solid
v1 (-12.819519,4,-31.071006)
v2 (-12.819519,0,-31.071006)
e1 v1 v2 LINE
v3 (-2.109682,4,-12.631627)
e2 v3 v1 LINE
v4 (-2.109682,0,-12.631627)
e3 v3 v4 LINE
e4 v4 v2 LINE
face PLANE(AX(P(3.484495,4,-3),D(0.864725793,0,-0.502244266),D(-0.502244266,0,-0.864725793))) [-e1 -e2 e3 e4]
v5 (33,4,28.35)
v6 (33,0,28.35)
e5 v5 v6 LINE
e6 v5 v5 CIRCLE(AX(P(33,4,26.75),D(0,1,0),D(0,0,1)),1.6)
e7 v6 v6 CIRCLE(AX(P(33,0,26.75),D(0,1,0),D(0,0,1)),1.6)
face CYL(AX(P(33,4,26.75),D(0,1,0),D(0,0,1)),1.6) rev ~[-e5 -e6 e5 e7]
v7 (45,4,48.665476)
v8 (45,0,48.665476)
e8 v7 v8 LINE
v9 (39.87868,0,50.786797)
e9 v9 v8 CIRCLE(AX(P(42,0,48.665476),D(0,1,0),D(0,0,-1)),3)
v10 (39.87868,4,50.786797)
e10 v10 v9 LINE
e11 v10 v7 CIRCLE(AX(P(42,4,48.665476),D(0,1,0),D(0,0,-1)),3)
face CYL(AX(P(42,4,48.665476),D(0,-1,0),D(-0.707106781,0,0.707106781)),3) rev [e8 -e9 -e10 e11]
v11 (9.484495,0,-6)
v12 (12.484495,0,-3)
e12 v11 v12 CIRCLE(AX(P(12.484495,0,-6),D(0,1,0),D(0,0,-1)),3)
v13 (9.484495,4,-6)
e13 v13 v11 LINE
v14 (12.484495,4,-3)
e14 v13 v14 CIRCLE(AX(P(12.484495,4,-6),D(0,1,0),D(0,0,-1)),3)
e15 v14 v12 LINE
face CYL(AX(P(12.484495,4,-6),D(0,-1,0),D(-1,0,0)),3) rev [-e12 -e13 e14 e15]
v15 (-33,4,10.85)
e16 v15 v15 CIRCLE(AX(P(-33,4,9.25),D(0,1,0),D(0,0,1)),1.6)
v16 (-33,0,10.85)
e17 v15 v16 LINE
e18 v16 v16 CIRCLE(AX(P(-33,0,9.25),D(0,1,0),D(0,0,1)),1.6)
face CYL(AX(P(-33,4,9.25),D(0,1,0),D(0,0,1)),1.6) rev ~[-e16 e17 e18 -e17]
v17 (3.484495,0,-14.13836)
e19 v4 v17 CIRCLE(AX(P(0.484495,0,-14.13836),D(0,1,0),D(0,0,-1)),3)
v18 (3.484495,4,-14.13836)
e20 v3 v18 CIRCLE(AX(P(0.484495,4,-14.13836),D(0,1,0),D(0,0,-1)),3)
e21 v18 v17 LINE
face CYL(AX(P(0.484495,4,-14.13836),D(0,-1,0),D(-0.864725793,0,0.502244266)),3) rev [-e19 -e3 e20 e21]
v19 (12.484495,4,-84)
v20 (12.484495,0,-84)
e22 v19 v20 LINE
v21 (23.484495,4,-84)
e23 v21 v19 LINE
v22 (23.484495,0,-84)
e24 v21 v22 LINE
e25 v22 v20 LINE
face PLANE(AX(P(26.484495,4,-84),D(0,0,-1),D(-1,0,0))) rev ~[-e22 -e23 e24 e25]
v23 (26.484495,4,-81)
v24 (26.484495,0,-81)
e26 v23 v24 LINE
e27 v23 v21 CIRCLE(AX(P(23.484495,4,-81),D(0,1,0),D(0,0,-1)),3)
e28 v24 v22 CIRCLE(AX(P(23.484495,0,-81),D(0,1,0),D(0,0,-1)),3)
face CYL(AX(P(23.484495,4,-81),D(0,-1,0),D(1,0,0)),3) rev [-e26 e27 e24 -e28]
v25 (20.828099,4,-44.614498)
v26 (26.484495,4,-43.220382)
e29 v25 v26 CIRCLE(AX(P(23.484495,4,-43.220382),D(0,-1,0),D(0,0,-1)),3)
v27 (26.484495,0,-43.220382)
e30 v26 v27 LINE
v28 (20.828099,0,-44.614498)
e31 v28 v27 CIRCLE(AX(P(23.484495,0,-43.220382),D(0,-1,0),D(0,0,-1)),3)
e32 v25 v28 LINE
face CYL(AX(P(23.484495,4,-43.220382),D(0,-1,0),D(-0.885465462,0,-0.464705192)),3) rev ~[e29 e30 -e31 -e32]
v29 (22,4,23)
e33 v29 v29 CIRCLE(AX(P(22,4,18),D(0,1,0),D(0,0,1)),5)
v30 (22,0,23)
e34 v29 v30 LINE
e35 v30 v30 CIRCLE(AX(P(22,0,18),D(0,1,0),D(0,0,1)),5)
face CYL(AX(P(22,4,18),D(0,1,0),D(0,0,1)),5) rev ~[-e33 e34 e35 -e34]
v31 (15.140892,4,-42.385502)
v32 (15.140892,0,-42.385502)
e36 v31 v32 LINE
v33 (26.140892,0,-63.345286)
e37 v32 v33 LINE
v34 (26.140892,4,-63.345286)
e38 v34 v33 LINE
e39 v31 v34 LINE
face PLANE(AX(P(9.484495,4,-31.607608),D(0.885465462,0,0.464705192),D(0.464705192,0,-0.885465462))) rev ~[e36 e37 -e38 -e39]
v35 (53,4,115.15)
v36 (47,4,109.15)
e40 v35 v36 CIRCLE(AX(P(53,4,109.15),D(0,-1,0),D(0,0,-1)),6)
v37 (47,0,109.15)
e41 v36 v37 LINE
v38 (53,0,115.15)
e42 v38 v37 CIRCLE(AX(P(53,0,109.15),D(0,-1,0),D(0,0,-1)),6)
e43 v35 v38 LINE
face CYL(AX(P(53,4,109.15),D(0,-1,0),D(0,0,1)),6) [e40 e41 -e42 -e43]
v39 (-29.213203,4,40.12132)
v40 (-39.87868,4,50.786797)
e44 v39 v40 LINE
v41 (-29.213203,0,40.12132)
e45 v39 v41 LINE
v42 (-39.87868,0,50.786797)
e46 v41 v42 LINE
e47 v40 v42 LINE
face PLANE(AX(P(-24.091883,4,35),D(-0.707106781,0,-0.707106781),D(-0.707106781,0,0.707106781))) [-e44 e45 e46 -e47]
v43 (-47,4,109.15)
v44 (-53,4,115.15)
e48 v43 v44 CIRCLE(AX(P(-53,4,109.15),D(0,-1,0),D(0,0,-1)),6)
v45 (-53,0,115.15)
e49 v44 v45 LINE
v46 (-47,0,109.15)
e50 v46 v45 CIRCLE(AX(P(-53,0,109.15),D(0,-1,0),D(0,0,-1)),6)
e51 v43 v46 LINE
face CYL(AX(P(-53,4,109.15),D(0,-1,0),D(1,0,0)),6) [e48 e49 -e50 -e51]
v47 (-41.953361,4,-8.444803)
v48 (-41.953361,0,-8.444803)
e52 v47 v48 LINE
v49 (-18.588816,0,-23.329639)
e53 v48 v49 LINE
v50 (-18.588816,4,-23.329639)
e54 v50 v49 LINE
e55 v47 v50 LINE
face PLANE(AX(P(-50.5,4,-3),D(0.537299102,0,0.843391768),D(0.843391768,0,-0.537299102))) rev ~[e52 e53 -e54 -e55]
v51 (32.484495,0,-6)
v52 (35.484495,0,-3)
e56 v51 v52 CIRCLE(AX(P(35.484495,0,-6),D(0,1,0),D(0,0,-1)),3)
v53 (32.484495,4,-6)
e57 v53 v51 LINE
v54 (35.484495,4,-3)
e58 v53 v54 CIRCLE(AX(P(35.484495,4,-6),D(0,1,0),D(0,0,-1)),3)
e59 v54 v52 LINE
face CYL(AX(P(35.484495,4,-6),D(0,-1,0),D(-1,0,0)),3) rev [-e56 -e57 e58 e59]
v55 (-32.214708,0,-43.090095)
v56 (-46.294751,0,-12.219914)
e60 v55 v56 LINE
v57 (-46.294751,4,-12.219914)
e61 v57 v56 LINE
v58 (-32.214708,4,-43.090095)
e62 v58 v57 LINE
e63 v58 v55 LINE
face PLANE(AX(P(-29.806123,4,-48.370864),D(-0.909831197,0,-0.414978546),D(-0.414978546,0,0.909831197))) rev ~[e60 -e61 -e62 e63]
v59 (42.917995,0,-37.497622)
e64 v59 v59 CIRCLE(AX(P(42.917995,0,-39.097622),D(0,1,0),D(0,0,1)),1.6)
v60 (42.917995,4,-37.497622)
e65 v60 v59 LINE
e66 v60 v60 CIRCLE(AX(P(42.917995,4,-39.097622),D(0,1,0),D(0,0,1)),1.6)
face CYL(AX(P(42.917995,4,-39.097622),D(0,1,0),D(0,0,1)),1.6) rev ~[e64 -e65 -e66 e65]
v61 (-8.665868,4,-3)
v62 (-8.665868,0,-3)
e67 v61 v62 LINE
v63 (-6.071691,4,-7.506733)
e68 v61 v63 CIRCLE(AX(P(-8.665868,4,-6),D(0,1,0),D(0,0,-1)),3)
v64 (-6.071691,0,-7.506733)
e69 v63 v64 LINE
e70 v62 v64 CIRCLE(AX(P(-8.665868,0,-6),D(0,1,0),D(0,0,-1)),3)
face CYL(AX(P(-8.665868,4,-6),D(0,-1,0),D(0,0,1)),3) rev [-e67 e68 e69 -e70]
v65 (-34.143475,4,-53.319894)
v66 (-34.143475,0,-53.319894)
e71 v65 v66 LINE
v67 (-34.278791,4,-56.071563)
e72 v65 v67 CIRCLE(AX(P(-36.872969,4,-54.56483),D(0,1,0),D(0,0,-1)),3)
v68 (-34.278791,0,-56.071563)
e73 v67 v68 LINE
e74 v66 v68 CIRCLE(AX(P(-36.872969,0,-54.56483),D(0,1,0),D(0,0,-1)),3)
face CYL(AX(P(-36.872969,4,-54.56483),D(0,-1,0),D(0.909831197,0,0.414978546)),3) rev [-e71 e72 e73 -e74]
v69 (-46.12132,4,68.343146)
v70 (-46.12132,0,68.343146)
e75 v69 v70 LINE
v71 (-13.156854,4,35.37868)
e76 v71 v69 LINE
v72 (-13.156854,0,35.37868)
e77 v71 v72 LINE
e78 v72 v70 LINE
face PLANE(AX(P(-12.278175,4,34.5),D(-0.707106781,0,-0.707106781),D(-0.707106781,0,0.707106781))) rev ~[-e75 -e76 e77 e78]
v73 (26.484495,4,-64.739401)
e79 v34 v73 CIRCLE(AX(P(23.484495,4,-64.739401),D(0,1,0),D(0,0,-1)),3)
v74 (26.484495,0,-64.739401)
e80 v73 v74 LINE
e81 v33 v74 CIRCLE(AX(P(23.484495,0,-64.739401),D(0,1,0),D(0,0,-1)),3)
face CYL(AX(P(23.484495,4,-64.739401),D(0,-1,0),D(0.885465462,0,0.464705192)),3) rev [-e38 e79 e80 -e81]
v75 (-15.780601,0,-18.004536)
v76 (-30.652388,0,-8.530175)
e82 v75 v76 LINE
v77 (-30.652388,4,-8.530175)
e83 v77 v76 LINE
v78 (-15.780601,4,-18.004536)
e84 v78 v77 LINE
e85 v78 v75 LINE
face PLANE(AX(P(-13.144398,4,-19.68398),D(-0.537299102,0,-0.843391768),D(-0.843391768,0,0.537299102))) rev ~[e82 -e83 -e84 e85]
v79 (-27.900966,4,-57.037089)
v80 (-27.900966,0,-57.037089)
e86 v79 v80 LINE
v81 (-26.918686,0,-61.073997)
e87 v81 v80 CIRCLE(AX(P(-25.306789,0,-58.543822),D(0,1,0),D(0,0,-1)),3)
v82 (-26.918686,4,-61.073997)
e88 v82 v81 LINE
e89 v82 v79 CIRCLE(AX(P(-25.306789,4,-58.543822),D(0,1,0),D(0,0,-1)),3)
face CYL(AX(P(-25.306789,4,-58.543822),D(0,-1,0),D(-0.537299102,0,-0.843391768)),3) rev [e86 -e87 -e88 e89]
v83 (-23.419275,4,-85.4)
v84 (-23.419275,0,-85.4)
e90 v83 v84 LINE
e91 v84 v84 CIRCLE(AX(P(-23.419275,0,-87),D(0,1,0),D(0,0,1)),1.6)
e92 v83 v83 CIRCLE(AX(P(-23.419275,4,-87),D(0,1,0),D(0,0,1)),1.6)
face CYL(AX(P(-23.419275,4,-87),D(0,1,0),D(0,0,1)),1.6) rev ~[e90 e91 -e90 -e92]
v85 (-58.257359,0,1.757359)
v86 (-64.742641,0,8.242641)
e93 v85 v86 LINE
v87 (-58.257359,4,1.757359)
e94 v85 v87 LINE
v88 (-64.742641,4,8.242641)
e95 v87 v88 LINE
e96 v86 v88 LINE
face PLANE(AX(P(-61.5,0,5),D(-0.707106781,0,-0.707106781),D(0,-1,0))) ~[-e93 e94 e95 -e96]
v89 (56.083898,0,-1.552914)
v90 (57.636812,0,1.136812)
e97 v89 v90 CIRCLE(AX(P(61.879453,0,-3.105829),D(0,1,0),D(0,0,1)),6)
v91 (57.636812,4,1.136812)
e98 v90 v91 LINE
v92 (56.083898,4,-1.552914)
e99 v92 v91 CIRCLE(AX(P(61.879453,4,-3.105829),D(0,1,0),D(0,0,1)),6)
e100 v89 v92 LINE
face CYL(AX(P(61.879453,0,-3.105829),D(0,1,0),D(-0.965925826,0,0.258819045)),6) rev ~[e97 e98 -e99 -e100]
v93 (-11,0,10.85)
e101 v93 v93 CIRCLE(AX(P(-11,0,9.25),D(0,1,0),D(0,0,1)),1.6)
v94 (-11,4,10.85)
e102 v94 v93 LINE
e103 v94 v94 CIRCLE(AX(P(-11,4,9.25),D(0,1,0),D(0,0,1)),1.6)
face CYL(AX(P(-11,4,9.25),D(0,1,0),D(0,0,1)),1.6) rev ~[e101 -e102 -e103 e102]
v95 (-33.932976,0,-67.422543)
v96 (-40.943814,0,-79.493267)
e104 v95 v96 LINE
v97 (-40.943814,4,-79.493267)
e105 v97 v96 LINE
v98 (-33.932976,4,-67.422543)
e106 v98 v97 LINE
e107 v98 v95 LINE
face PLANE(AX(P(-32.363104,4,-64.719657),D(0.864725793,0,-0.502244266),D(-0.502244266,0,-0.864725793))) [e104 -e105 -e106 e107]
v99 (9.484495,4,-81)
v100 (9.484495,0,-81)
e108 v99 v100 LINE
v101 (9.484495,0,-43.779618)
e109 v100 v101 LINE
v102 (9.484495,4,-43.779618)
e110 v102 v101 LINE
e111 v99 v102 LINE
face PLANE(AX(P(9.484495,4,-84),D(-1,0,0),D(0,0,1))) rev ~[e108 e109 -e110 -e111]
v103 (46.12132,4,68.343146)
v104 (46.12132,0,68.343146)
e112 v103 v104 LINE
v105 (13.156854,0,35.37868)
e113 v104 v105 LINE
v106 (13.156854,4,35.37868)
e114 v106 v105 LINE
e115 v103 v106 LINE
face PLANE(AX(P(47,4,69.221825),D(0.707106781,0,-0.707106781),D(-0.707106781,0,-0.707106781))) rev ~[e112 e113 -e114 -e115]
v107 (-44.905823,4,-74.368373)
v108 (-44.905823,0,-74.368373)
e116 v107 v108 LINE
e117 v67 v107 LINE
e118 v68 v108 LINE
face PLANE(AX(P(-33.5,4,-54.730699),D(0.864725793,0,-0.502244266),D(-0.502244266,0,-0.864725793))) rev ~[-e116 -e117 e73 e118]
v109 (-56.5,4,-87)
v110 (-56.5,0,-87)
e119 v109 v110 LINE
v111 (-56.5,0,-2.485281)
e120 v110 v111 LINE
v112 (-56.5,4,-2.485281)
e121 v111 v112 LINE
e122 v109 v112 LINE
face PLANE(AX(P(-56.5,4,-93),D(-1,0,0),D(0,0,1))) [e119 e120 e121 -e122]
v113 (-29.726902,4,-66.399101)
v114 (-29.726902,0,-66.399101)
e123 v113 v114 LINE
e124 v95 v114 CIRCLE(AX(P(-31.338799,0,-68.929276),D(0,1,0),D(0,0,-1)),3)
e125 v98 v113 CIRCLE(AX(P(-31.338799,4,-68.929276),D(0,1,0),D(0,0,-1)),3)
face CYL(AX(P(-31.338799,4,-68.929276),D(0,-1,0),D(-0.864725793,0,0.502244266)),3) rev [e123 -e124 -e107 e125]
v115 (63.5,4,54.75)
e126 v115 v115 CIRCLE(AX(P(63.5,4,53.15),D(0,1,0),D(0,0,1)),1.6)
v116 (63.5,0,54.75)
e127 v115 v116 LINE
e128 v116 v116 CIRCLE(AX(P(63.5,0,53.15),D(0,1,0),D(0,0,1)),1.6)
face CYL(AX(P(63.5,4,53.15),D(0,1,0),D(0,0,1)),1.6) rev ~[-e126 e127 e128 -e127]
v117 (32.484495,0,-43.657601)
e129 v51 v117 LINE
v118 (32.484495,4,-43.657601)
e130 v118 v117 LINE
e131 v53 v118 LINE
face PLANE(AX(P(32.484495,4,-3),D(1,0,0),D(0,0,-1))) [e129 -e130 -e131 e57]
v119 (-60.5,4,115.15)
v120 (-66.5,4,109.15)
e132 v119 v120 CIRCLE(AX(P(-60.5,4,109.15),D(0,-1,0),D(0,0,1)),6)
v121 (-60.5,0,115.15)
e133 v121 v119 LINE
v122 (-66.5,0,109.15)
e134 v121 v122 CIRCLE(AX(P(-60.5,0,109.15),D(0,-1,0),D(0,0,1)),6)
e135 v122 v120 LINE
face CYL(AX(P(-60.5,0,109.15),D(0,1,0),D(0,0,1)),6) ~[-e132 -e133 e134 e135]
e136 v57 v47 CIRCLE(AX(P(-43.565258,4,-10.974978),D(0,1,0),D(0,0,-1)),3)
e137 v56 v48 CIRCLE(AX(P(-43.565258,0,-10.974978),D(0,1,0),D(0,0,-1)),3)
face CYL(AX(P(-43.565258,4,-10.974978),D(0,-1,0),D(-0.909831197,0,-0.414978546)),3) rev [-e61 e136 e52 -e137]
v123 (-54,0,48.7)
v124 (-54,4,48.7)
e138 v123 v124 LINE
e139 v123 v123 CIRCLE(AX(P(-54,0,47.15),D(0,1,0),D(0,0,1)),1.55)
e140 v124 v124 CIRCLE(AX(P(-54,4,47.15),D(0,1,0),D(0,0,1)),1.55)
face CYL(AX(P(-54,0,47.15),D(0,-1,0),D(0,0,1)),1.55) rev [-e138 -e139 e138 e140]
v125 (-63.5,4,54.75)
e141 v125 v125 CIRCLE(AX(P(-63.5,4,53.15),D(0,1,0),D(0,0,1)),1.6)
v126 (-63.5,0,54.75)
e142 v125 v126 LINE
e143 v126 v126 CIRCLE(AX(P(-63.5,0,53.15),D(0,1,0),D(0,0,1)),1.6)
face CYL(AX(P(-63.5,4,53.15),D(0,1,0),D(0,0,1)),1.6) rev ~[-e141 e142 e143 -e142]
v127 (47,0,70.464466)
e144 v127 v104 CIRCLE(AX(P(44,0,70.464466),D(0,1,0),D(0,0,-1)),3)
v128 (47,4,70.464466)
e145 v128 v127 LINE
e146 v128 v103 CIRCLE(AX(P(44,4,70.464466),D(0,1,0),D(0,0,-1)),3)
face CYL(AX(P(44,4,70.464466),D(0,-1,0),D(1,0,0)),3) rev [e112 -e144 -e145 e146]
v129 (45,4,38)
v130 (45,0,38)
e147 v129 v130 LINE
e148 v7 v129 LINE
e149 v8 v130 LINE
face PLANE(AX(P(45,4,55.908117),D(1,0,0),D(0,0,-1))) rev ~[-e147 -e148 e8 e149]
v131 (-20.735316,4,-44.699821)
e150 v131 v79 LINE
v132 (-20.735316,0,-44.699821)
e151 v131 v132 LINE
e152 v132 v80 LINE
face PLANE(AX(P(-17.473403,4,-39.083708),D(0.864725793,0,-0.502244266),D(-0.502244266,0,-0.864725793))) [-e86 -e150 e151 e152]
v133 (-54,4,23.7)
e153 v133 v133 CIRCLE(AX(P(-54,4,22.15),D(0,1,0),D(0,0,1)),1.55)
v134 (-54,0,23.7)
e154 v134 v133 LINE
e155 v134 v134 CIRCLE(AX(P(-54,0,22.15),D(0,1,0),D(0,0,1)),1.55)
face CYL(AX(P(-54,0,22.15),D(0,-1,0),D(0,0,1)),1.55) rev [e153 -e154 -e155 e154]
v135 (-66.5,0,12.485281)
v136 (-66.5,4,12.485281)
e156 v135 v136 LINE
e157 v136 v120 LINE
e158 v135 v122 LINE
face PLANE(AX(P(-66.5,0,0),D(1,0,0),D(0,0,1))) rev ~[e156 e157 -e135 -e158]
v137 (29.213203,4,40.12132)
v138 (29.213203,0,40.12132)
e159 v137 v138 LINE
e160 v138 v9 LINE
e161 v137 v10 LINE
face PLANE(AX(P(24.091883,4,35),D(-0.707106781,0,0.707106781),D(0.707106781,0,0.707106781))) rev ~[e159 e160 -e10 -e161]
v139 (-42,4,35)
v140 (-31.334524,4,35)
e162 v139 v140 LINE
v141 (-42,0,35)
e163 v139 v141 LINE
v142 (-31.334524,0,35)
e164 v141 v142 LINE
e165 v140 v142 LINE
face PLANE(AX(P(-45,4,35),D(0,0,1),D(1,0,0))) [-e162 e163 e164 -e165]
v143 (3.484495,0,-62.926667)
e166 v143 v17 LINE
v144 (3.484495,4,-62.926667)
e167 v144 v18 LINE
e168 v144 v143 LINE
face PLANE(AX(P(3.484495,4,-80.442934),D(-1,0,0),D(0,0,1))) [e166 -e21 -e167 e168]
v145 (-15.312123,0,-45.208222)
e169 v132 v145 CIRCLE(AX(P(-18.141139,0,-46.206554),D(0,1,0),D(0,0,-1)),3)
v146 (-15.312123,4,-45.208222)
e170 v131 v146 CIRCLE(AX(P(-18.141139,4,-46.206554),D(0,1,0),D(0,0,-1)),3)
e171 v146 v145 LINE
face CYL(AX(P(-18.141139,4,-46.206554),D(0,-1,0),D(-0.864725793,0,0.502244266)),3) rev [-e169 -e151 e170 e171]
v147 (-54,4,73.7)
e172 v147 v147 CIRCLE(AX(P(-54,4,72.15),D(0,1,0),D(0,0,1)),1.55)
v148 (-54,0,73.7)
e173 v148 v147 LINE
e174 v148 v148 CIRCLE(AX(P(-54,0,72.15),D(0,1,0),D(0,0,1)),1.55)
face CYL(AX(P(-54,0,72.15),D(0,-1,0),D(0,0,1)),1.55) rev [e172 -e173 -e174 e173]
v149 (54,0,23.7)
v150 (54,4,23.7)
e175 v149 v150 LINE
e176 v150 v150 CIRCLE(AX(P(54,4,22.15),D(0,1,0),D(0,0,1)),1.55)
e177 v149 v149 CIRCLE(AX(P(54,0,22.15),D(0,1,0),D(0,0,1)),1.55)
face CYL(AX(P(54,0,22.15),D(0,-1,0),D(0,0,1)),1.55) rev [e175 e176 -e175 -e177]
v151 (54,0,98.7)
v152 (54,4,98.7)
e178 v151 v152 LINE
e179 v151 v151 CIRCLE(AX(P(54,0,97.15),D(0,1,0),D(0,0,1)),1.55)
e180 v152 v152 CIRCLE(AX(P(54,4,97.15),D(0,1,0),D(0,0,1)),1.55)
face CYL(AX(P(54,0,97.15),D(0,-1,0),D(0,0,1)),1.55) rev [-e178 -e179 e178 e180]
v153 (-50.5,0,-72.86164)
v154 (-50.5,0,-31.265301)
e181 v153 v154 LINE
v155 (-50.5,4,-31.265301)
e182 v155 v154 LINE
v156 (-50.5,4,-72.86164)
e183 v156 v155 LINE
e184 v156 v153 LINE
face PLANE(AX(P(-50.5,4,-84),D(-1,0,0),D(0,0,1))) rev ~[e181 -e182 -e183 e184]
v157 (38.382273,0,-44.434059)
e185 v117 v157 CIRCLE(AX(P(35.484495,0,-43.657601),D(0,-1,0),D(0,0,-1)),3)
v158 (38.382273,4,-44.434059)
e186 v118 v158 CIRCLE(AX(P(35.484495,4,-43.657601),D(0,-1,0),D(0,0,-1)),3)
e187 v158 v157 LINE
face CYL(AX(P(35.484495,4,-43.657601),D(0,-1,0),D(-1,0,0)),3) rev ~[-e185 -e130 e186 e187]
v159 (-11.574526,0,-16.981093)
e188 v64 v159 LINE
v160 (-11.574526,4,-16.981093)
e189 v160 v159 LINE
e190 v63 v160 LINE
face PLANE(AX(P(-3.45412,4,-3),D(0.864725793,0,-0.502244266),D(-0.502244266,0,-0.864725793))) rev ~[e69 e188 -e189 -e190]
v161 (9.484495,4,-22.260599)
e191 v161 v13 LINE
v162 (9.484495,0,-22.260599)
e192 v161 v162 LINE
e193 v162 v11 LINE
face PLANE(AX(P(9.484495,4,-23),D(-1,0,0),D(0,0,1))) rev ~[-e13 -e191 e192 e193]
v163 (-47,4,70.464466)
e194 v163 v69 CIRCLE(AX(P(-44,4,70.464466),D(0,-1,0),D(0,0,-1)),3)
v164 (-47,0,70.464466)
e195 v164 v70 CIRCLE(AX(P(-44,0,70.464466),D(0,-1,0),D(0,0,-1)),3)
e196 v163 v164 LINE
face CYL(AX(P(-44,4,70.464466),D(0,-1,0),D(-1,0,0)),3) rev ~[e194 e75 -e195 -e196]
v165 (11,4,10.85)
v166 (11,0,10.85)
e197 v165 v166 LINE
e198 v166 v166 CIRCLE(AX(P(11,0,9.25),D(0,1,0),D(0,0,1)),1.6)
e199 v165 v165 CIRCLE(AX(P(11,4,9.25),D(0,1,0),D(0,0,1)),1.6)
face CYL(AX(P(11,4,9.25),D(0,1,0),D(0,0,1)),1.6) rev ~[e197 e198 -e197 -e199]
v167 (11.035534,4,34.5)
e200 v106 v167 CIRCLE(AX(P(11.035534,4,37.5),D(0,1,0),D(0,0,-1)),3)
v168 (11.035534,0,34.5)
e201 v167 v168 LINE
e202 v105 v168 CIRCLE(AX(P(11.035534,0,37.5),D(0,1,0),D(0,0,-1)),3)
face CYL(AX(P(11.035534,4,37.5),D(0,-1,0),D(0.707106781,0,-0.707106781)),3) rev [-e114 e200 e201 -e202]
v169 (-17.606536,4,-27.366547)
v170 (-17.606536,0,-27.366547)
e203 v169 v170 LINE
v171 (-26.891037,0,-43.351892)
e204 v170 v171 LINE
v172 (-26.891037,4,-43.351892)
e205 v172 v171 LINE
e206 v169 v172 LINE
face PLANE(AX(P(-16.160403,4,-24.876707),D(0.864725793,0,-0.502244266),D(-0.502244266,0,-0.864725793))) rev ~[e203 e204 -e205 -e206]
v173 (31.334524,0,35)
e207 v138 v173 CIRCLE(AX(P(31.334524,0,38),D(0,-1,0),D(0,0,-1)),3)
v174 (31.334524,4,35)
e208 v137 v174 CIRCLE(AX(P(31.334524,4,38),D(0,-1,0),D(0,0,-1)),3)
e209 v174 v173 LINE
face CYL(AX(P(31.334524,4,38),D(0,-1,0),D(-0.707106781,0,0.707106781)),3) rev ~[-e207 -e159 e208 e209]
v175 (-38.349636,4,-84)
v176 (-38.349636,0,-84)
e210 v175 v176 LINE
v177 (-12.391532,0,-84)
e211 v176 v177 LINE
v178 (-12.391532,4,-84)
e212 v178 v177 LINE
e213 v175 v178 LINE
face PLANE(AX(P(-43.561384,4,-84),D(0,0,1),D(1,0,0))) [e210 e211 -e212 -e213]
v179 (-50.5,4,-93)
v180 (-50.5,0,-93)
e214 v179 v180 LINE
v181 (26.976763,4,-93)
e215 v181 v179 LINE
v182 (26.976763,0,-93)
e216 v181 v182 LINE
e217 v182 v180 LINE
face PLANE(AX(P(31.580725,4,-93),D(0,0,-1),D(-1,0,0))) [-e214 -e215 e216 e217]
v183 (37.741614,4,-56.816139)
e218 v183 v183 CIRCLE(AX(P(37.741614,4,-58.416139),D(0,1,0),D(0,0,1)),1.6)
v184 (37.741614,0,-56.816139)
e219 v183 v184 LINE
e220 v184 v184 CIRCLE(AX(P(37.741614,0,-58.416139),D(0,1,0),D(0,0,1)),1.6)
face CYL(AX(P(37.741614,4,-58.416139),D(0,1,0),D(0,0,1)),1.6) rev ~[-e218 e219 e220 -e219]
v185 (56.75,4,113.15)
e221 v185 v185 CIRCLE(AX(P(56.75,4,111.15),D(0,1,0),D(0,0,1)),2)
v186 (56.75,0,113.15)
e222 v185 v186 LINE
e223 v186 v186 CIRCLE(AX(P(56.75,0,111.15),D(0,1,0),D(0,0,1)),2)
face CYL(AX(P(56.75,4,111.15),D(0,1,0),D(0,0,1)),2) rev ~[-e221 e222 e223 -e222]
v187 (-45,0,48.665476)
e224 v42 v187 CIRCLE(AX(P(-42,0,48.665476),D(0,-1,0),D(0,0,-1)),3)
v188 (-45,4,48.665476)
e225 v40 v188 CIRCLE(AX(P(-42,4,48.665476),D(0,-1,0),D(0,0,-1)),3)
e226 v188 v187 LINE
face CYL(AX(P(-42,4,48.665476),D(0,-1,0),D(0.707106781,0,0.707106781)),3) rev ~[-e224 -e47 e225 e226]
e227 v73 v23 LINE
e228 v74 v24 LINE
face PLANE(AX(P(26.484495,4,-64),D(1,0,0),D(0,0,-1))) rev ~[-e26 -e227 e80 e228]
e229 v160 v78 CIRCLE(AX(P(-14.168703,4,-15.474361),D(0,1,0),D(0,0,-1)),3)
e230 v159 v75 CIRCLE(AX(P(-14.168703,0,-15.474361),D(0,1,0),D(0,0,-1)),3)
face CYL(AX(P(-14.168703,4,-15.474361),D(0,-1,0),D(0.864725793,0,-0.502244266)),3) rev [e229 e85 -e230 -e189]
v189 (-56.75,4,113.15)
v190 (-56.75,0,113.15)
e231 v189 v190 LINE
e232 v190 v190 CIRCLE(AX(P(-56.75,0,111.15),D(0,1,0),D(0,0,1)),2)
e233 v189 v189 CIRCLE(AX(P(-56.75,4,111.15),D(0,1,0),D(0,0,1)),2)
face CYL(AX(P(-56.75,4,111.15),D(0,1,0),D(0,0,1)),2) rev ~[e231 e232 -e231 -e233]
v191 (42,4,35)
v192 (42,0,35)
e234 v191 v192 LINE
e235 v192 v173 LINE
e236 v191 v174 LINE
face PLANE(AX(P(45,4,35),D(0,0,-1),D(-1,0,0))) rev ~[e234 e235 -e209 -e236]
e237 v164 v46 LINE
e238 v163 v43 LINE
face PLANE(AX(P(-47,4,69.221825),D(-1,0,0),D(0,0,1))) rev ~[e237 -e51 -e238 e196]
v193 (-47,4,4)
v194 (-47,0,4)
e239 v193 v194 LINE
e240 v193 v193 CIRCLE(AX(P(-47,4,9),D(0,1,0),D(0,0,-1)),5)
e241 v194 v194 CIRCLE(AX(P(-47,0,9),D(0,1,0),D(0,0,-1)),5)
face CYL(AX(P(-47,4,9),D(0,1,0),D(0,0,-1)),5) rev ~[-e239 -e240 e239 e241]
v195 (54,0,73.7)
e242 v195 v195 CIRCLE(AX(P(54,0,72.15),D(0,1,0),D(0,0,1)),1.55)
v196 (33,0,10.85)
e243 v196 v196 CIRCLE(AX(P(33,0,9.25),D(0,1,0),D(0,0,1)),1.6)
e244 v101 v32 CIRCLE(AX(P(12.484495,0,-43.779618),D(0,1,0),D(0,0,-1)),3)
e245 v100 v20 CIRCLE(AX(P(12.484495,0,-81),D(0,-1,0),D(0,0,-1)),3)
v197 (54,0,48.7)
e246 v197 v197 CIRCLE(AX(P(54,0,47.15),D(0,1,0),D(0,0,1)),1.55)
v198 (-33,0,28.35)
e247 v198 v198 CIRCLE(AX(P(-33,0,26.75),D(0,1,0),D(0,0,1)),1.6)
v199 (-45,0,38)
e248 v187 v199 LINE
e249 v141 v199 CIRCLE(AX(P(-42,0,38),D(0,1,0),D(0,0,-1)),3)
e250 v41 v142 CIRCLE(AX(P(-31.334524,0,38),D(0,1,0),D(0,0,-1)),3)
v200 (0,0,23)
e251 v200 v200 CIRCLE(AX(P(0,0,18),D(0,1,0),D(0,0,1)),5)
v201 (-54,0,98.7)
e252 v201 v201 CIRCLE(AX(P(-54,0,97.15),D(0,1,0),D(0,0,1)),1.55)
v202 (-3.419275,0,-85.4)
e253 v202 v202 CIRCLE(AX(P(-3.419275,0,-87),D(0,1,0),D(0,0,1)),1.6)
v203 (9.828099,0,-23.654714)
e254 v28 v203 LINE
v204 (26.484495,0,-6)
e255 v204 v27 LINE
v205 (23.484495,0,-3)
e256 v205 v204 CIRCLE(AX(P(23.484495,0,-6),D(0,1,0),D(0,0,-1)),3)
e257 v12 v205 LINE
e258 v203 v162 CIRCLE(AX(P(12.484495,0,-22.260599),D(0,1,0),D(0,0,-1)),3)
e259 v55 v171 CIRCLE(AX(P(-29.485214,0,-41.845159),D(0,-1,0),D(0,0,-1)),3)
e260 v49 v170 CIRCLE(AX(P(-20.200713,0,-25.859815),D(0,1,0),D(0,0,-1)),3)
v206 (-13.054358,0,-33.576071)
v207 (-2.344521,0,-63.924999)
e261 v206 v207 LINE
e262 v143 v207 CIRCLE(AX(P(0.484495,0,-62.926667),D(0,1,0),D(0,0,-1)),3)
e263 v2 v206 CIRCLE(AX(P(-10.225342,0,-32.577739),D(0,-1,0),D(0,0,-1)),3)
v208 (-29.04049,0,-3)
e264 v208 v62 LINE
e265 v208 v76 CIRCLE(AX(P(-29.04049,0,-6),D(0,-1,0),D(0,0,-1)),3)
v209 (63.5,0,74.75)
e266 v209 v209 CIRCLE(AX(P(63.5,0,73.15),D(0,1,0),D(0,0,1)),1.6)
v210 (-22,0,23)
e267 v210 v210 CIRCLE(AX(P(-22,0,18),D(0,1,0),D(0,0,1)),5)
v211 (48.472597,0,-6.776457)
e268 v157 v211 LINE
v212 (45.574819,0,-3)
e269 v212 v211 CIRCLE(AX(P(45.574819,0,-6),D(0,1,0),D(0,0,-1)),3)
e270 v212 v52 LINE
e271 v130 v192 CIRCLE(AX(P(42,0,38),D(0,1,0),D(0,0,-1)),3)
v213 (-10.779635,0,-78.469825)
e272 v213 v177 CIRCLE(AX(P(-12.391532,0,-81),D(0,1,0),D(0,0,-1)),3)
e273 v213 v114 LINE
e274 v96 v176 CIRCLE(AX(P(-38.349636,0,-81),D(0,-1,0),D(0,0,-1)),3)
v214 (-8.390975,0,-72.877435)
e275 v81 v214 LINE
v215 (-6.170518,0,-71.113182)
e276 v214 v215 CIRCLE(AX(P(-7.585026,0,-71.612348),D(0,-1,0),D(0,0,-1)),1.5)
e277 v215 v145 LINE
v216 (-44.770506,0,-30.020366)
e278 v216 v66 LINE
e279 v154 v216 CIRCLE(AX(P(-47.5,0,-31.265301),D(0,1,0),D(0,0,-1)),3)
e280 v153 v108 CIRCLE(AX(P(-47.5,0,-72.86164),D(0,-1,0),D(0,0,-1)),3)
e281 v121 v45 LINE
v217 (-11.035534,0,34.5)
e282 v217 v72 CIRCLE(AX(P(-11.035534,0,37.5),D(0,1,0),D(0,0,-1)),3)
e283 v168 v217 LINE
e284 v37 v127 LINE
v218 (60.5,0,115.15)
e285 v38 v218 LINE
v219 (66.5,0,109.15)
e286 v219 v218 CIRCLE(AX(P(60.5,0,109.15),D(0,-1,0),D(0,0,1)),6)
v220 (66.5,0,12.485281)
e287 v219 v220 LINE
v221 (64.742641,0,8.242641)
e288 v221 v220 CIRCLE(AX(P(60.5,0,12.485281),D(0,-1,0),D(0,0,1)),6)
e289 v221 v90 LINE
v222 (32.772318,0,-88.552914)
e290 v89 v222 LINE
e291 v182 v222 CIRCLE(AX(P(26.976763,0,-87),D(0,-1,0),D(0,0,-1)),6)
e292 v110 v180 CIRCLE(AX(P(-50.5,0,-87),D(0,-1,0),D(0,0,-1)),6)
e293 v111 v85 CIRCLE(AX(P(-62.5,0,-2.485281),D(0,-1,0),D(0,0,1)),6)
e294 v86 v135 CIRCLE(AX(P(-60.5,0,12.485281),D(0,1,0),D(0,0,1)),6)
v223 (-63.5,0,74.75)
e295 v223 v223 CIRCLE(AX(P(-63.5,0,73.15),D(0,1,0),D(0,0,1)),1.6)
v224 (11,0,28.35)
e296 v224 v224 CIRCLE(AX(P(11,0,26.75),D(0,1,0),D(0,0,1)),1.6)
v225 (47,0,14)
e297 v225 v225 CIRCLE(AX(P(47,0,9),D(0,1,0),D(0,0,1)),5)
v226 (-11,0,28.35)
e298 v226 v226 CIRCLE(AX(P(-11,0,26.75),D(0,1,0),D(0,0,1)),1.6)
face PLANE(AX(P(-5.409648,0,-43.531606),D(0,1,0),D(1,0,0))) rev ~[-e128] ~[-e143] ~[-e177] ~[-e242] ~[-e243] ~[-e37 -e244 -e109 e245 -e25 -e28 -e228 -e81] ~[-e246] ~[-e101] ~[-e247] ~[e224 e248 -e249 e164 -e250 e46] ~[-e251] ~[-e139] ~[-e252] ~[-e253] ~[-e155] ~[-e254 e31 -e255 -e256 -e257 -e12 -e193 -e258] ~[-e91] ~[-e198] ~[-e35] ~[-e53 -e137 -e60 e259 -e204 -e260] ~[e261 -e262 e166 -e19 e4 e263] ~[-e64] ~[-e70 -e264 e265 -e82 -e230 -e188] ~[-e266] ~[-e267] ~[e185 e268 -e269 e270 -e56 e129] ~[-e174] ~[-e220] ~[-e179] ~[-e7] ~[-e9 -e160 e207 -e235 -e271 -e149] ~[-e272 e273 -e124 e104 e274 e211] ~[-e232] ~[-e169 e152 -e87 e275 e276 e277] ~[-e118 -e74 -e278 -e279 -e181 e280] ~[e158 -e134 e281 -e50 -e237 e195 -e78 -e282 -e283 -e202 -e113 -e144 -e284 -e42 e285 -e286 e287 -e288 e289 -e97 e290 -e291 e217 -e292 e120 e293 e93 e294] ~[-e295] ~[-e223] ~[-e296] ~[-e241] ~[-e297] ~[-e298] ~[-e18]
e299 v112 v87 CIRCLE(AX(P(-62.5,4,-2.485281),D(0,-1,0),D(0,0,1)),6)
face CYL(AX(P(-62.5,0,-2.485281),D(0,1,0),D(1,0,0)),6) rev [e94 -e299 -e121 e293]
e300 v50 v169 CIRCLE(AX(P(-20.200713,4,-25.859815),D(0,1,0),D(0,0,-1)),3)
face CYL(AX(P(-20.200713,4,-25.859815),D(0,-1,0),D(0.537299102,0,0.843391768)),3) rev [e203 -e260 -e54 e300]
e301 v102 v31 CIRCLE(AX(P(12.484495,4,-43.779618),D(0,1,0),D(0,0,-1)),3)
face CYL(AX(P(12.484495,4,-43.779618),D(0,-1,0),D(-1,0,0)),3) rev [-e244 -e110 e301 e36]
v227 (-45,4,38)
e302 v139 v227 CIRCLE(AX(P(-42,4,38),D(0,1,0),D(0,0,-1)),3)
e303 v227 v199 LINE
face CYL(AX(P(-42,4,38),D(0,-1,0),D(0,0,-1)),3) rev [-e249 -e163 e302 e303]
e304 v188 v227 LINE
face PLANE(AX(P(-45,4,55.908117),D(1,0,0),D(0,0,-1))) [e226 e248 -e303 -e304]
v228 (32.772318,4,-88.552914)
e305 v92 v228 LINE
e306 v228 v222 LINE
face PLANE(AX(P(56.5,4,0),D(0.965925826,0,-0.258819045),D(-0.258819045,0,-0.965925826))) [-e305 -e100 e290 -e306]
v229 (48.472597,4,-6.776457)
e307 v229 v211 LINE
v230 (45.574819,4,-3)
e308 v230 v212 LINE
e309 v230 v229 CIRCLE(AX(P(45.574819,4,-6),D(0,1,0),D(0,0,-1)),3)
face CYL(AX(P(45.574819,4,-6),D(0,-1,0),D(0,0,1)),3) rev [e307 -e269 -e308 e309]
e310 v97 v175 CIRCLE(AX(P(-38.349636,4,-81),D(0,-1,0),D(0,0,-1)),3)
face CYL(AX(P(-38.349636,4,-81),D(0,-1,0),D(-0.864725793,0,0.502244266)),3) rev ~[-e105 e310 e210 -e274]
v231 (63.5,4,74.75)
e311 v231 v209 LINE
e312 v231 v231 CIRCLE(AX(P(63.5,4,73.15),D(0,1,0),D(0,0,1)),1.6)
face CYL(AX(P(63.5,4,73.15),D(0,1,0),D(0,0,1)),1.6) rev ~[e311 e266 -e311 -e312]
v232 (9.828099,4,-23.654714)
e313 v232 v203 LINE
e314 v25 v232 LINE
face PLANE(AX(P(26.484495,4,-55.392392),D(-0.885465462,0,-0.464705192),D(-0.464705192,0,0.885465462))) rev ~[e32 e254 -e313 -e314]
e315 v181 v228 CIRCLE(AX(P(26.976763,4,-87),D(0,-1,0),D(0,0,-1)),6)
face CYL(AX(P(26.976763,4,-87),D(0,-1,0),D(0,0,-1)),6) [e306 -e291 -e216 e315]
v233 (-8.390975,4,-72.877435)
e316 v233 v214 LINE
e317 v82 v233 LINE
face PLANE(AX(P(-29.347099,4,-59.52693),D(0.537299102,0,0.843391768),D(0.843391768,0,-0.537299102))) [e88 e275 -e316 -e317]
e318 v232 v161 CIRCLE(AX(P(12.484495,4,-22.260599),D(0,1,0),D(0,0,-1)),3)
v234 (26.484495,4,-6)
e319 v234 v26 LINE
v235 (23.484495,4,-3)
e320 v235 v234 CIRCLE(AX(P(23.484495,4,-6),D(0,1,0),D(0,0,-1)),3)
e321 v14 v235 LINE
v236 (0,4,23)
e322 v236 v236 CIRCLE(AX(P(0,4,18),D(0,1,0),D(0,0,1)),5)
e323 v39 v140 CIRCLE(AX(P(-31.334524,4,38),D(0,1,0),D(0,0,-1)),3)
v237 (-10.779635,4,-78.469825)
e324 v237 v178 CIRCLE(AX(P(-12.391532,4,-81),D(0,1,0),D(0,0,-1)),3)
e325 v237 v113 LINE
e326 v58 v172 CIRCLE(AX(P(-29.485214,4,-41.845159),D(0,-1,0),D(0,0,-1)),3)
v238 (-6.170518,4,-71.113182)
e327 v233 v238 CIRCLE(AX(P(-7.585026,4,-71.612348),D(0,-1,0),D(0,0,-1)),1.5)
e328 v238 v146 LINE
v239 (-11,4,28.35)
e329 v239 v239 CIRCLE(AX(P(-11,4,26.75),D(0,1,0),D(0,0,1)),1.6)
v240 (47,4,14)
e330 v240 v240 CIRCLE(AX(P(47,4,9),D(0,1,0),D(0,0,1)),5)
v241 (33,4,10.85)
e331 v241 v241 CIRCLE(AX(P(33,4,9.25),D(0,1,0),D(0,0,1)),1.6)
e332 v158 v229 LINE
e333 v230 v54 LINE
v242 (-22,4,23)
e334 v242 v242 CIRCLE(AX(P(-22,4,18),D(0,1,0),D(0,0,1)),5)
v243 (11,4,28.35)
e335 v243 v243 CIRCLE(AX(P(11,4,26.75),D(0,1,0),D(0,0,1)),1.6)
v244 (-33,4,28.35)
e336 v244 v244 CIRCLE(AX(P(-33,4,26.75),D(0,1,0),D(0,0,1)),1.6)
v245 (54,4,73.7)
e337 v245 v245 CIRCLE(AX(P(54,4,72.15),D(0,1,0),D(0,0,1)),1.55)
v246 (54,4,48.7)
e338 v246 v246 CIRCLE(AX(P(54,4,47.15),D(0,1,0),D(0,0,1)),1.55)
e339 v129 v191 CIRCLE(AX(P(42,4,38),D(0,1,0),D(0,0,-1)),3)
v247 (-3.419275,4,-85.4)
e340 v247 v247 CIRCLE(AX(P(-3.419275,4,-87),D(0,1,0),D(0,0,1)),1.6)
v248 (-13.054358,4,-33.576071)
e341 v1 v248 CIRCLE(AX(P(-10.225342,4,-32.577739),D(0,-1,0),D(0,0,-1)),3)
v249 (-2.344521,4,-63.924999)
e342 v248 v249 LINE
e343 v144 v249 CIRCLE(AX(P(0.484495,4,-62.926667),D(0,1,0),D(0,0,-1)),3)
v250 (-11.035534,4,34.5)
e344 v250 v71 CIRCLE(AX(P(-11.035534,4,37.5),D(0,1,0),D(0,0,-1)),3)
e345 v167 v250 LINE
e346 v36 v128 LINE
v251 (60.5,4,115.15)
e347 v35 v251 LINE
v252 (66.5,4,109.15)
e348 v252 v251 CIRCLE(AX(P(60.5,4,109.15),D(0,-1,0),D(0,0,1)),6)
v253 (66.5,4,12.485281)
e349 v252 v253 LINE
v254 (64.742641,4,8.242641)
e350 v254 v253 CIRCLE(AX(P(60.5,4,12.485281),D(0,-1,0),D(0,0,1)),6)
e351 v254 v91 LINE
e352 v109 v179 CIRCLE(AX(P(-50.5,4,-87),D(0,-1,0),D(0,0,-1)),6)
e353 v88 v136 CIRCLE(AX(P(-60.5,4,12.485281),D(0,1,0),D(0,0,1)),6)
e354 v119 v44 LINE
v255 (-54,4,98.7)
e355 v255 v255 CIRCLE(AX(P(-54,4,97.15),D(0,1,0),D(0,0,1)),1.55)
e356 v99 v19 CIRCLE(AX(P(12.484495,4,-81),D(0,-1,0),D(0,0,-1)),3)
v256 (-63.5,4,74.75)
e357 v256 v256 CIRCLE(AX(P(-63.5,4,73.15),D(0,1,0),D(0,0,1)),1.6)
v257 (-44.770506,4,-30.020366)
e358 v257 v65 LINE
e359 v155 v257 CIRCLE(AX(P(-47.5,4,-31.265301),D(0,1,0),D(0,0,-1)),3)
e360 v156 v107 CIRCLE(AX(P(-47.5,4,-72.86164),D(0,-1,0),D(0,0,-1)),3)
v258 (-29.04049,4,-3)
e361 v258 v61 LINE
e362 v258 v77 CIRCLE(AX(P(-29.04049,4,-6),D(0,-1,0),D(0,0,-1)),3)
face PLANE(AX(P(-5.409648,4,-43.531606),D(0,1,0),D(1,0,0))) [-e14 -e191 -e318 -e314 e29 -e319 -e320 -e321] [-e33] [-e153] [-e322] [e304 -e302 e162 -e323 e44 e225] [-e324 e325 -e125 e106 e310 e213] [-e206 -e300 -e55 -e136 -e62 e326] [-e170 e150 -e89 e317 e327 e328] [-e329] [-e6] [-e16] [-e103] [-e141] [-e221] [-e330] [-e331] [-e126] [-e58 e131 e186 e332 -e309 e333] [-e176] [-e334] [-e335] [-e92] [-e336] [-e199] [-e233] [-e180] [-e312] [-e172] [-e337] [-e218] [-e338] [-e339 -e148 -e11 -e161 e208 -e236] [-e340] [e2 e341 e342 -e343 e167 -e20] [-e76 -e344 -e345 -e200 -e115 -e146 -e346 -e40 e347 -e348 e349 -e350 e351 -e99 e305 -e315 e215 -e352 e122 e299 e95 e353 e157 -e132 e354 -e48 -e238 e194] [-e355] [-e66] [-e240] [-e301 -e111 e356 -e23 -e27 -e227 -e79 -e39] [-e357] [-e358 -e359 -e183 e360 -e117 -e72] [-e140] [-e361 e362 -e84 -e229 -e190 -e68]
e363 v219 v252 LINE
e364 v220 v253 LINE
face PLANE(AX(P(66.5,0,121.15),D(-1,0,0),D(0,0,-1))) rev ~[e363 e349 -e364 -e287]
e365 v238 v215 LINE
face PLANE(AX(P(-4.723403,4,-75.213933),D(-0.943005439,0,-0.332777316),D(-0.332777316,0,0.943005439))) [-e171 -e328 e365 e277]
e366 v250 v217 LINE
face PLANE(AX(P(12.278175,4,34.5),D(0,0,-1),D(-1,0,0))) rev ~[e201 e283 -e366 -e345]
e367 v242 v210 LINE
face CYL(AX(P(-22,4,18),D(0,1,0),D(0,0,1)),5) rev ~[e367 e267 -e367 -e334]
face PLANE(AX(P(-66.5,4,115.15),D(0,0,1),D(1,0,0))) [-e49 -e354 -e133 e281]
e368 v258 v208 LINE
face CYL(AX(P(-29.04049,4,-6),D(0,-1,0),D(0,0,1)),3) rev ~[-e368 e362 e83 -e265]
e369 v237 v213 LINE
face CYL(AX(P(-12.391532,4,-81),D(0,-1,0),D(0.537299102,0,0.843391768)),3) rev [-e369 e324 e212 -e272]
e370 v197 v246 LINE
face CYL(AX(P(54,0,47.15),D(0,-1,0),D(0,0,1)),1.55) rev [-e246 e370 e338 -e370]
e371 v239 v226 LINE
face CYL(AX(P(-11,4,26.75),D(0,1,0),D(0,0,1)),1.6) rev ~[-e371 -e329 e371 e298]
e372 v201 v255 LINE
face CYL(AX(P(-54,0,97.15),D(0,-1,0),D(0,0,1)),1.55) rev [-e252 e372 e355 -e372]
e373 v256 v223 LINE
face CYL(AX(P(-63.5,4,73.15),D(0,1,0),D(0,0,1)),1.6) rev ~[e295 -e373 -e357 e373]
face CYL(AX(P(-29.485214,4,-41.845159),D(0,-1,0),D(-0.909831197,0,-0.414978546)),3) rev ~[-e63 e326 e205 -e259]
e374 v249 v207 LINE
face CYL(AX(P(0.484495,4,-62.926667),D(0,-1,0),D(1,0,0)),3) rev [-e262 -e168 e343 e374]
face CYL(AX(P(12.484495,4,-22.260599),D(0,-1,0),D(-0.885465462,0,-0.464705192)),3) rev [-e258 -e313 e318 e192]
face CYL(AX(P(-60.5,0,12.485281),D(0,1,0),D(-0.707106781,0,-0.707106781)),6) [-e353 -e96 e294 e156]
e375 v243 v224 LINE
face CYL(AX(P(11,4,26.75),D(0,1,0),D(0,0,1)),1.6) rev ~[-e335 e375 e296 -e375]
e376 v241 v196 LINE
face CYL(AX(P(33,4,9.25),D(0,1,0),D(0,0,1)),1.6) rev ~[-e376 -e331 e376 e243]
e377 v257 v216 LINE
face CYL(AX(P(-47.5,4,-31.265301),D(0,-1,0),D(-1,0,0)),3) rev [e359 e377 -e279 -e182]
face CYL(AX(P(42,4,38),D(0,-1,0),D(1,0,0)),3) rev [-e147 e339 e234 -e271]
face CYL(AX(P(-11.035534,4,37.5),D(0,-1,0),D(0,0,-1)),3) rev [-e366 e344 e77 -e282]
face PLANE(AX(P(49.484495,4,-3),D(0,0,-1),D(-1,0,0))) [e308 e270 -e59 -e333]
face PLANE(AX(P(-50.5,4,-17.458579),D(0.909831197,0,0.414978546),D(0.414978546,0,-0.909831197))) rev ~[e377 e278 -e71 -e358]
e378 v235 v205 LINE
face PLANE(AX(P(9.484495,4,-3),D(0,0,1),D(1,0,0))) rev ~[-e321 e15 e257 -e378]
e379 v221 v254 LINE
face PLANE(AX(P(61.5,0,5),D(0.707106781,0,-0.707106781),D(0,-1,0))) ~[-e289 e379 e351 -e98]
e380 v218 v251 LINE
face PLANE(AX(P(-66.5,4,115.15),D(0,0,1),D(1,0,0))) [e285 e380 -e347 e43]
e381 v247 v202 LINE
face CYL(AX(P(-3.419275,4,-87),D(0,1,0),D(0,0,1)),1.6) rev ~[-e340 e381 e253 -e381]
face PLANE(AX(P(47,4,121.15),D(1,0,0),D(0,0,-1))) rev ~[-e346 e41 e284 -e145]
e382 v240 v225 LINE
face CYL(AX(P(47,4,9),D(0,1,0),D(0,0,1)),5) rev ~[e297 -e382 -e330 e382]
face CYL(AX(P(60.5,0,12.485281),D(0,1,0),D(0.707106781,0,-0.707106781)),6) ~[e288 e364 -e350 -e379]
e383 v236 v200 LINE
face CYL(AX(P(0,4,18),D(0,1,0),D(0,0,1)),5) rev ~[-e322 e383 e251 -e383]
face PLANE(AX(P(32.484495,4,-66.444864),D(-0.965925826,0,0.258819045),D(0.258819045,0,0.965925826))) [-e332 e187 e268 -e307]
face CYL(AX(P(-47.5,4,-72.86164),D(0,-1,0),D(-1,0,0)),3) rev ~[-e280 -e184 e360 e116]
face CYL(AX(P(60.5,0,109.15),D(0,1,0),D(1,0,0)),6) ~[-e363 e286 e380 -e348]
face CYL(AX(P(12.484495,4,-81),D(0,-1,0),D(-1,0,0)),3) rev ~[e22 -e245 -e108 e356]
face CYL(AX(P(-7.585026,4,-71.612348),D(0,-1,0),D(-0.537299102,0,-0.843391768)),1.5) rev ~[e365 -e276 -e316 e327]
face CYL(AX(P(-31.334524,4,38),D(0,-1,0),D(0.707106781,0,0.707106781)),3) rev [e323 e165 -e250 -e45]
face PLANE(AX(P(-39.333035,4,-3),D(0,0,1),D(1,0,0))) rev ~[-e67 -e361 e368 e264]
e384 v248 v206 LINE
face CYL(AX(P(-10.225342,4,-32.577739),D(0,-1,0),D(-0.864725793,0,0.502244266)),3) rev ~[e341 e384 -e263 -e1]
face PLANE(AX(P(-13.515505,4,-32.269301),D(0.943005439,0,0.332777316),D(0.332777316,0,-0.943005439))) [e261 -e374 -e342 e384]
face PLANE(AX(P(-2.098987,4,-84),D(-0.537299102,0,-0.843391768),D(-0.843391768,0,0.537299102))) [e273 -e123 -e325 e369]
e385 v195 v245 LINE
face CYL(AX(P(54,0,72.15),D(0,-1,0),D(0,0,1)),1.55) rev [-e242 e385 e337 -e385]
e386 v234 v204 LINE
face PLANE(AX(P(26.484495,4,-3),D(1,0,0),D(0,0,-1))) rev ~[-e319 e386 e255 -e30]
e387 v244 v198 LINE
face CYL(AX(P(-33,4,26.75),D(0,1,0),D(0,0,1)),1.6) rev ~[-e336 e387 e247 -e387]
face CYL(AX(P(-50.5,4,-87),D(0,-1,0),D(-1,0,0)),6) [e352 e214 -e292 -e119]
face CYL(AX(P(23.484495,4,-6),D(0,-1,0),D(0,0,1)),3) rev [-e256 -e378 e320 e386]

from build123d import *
from OCP.BRepFilletAPI import BRepFilletAPI_MakeFillet

# Parameters (mm, degrees)
SKETCH_1_R          = 1.55
EXTRUDE_1_DEPTH     = 4
CUT_EXTRUDE_1_DEPTH = 139.25907746
CUT_EXTRUDE_2_DEPTH = 420
FILLET_1_R          = 3
SKETCH_4_R          = 1.6
CUT_EXTRUDE_3_DEPTH = 139.25907746
SKETCH_5_R          = 1.6
CUT_EXTRUDE_4_DEPTH = 10
CHAMFER_1_SIZE      = 10
EXTRUDE_2_DEPTH     = 4
SKETCH_8_R          = 1.6
CUT_EXTRUDE_6_DEPTH = 4
FILLET_2_R          = 6
SKETCH_7_R          = 5
CUT_EXTRUDE_5_DEPTH = 4
FILLET_3_R1         = 3
FILLET_3_R2         = 1.5
SKETCH_9_R          = 2
SKETCH_9_W          = 133
SKETCH_9_H          = 6
CUT_EXTRUDE_7_DEPTH = 10
FILLET_4_R          = 6


with BuildPart() as part:
    # 草图1 → 凸台-拉伸1 (new body)
    with BuildSketch(Plane(origin=(0, 0, 0), x_dir=(1, 0, 0), z_dir=(0, 1, 0))):
        Polygon((66.5, 0), (-66.5, 0), (-66.5, -121.15), (-41.5, -121.15), (-41.5, -71.5), (-10, -40), (10, -40), (41.5, -71.5), (41.5, -121.15), (66.5, -121.15), align=None)
        with Locations(Location((-54, -22.15, 0), (0, 0, 270))):
            Circle(SKETCH_1_R, mode=Mode.SUBTRACT)
        with Locations(Location((54, -22.15, 0), (0, 0, 270))):
            Circle(SKETCH_1_R, mode=Mode.SUBTRACT)
        with Locations(Location((-54, -47.15, 0), (0, 0, 270))):
            Circle(SKETCH_1_R, mode=Mode.SUBTRACT)
        with Locations(Location((54, -47.15, 0), (0, 0, 270))):
            Circle(SKETCH_1_R, mode=Mode.SUBTRACT)
        with Locations(Location((-54, -72.15, 0), (0, 0, 270))):
            Circle(SKETCH_1_R, mode=Mode.SUBTRACT)
        with Locations(Location((54, -72.15, 0), (0, 0, 270))):
            Circle(SKETCH_1_R, mode=Mode.SUBTRACT)
        with Locations(Location((-54, -97.15, 0), (0, 0, 270))):
            Circle(SKETCH_1_R, mode=Mode.SUBTRACT)
        with Locations(Location((54, -97.15, 0), (0, 0, 270))):
            Circle(SKETCH_1_R, mode=Mode.SUBTRACT)
    extrude(amount=EXTRUDE_1_DEPTH)

    # 草图2 → 切除-拉伸1 (cut, through all)
    with BuildSketch(Plane(origin=(0, 4, 0), x_dir=(1, 0, 0), z_dir=(0, 1, 0))):
        Polygon((-47, -115.65), (-47, -121.15), (47, -121.15), (47, -115.65), (47, -69.221825407), (12.278174593, -34.5), (-12.278174593, -34.5), (-47, -69.221825407), align=None)
    extrude(amount=-CUT_EXTRUDE_1_DEPTH, mode=Mode.SUBTRACT)

    # 草图3 → 切除-拉伸2 (cut)
    with BuildSketch(Plane(origin=(0, 4, 0), x_dir=(1, 0, 0), z_dir=(0, 1, 0))):
        Polygon((-45, -55.908116908), (-45, -35), (-24.091883092, -35), align=None)
        Polygon((24.091883092, -35), (45, -55.908116908), (45, -35), align=None)
    extrude(amount=-CUT_EXTRUDE_2_DEPTH, mode=Mode.SUBTRACT)

    # 圆角1
    fillet_1_edges = [part.edges().sort_by_distance(p)[0] for p in [
        (-24.091883092, 2, 35),
        (-45, 2, 55.908116908),
        (-45, 2, 35),
        (24.091883092, 2, 35),
        (45, 2, 35),
        (45, 2, 55.908116908),
        (-47, 2, 69.221825407),
        (-12.278174593, 2, 34.5),
        (12.278174593, 2, 34.5),
        (47, 2, 69.221825407),
    ]]
    fillet(fillet_1_edges, radius=FILLET_1_R)

    # 草图4 → 切除-拉伸3 (cut, through all)
    with BuildSketch(Plane(origin=(0, 4, 0), x_dir=(1, 0, 0), z_dir=(0, 1, 0))):
        with Locations(Location((-33, -26.75, 0), (0, 0, 270))):
            Circle(SKETCH_4_R)
        with Locations(Location((33, -26.75, 0), (0, 0, 270))):
            Circle(SKETCH_4_R)
        with Locations(Location((-33, -9.25, 0), (0, 0, 270))):
            Circle(SKETCH_4_R)
        with Locations(Location((11, -9.25, 0), (0, 0, 270))):
            Circle(SKETCH_4_R)
        with Locations(Location((-11, -9.25, 0), (0, 0, 270))):
            Circle(SKETCH_4_R)
        with Locations(Location((33, -9.25, 0), (0, 0, 270))):
            Circle(SKETCH_4_R)
        with Locations(Location((11, -26.75, 0), (0, 0, 270))):
            Circle(SKETCH_4_R)
        with Locations(Location((-11, -26.75, 0), (0, 0, 270))):
            Circle(SKETCH_4_R)
    extrude(amount=-CUT_EXTRUDE_3_DEPTH, mode=Mode.SUBTRACT)

    # 草图5 → 切除-拉伸4 (cut)
    with BuildSketch(Plane(origin=(0, 4, 0), x_dir=(1, 0, 0), z_dir=(0, 1, 0))):
        with Locations(Location((-63.5, -53.15, 0), (0, 0, 270))):
            Circle(SKETCH_5_R)
        with Locations(Location((63.5, -53.15, 0), (0, 0, 270))):
            Circle(SKETCH_5_R)
        with Locations(Location((-63.5, -73.15, 0), (0, 0, 270))):
            Circle(SKETCH_5_R)
        with Locations(Location((63.5, -73.15, 0), (0, 0, 270))):
            Circle(SKETCH_5_R)
    extrude(amount=-CUT_EXTRUDE_4_DEPTH, mode=Mode.SUBTRACT)

    # 倒角1
    chamfer_1_edges = [part.edges().sort_by_distance(p)[0] for p in [
        (-66.5, 2, 0),
        (66.5, 2, 0),
    ]]
    chamfer(chamfer_1_edges, length=CHAMFER_1_SIZE)

    # 草图6 → 凸台-拉伸2 (add)
    with BuildSketch(Plane(origin=(0, 4, 0), x_dir=(1, 0, 0), z_dir=(0, 1, 0))):
        Polygon((-56.5, 93), (-56.5, 0), (56.5, 0), (31.580725104, 93), align=None)
    extrude(amount=-EXTRUDE_2_DEPTH)

    # 草图8 → 切除-拉伸6 (cut)
    with BuildSketch(Plane(origin=(0, 4, 0), x_dir=(1, 0, 0), z_dir=(0, 1, 0))):
        with Locations(Location((-23.419274896, 87, 0), (0, 0, 270))):
            Circle(SKETCH_8_R)
        with Locations(Location((-3.419274896, 87, 0), (0, 0, 270))):
            Circle(SKETCH_8_R)
        with Locations(Location((37.741614204, 58.416138945, 0), (0, 0, 270))):
            Circle(SKETCH_8_R)
        with Locations(Location((42.917995106, 39.097622419, 0), (0, 0, 270))):
            Circle(SKETCH_8_R)
    extrude(amount=-CUT_EXTRUDE_6_DEPTH, mode=Mode.SUBTRACT)

    # 圆角2
    fillet_2_edges = [part.edges().sort_by_distance(p)[0] for p in [
        (66.5, 2, 121.15),
        (-66.5, 2, 121.15),
        (-56.5, 2, 0),
        (56.5, 2, 0),
        (66.5, 2, 10),
        (-66.5, 2, 10),
        (-56.5, 2, -93),
        (31.580725104, 2, -93),
        (47, 2, 121.15),
        (-47, 2, 121.15),
    ]]
    fillet(fillet_2_edges, radius=FILLET_2_R)

    # 草图7 → 切除-拉伸5 (cut)
    with BuildSketch(Plane(origin=(0, 4, 0), x_dir=(1, 0, 0), z_dir=(0, 1, 0))):
        with Locations(Location((-22, -18, 0), (0, 0, 270))):
            Circle(SKETCH_7_R)
        with Locations(Location((0, -18, 0), (0, 0, 270))):
            Circle(SKETCH_7_R)
        with Locations(Location((22, -18, 0), (0, 0, 270))):
            Circle(SKETCH_7_R)
        with Locations(Location((47, -9, 0), (0, 0, 270))):
            Circle(SKETCH_7_R)
        with Locations(Location((-47, -9, 0), (0, 0, 90))):
            Circle(SKETCH_7_R)
        Polygon((-50.5, 84), (-50.5, 17.458578786), (-33.5, 54.730699229), align=None)
        Polygon((-39.333035497, 3), (-3.454120401, 3), (-13.144398267, 19.683979847), align=None)
        Polygon((-43.561384259, 84), (-2.098986911, 84), (-32.36310387, 64.719656659), align=None)
        Polygon((-4.723403201, 75.213933081), (-17.473403201, 39.083707996), (-29.347098825, 59.52692967), align=None)
        Polygon((-13.51550466, 32.269300771), (3.48449534, 80.442934218), (3.48449534, 3), align=None)
        Polygon((9.48449534, 84), (9.48449534, 31.60760773), (26.48449534, 64), (26.48449534, 84), align=None)
        Polygon((32.48449534, 66.444863729), (49.48449534, 3), (32.48449534, 3), align=None)
        Polygon((26.48449534, 55.39239227), (9.48449534, 23), (9.48449534, 3), (26.48449534, 3), align=None)
        Polygon((-29.80612279, 48.370863754), (-50.5, 3), (-16.160403312, 24.876706835), align=None)
    extrude(amount=-CUT_EXTRUDE_5_DEPTH, mode=Mode.SUBTRACT)

    # 圆角3: one fillet with a radius per group of edges: ONE call of the kernel's fillet builder (fillet() takes one radius for all edges)
    fillet_3_edges_1 = [part.edges().sort_by_distance(p)[0] for p in [
        (26.48449534, 2, -84),
        (9.48449534, 2, -84),
        (9.48449534, 2, -31.60760773),
        (26.48449534, 2, -64),
        (-13.51550466, 2, -32.269300771),
        (3.48449534, 2, -3),
        (3.48449534, 2, -80.442934218),
        (-17.473403201, 2, -39.083707996),
        (-3.454120401, 2, -3),
        (32.48449534, 2, -66.444863729),
        (32.48449534, 2, -3),
        (49.48449534, 2, -3),
        (26.48449534, 2, -3),
        (26.48449534, 2, -55.39239227),
        (9.48449534, 2, -23),
        (9.48449534, 2, -3),
        (-33.5, 2, -54.730699229),
        (-50.5, 2, -84),
        (-50.5, 2, -17.458578786),
        (-43.561384259, 2, -84),
        (-29.347098825, 2, -59.52692967),
        (-13.144398267, 2, -19.683979847),
        (-39.333035497, 2, -3),
        (-32.36310387, 2, -64.719656659),
        (-2.098986911, 2, -84),
        (-16.160403312, 2, -24.876706835),
        (-29.80612279, 2, -48.370863754),
        (-50.5, 2, -3),
    ]]
    fillet_3_edges_2 = [part.edges().sort_by_distance(p)[0] for p in [
        (-4.723403201, 2, -75.213933081),
    ]]
    fillet_3 = BRepFilletAPI_MakeFillet(part.part.solid().wrapped)
    for e in fillet_3_edges_1:
        fillet_3.Add(FILLET_3_R1, e.wrapped)
    for e in fillet_3_edges_2:
        fillet_3.Add(FILLET_3_R2, e.wrapped)
    add(Compound.cast(fillet_3.Shape()), mode=Mode.REPLACE)

    # 草图9 → 切除-拉伸7 (cut)
    with BuildSketch(Plane(origin=(0, 4, 0), x_dir=(1, 0, 0), z_dir=(0, 1, 0))):
        with Locations(Location((-56.75, -111.15, 0), (0, 0, 270))):
            Circle(SKETCH_9_R)
        with Locations(Location((56.75, -111.15, 0), (0, 0, 270))):
            Circle(SKETCH_9_R)
        with Locations((0, -118.15)):
            Rectangle(SKETCH_9_W, SKETCH_9_H)
    extrude(amount=-CUT_EXTRUDE_7_DEPTH, mode=Mode.SUBTRACT)

    # 圆角4
    fillet_4_edges = [part.edges().sort_by_distance(p)[0] for p in [
        (66.5, 2, 115.15),
        (47, 2, 115.15),
        (-47, 2, 115.15),
        (-66.5, 2, 115.15),
    ]]
    fillet(fillet_4_edges, radius=FILLET_4_R)


solid = part.part
